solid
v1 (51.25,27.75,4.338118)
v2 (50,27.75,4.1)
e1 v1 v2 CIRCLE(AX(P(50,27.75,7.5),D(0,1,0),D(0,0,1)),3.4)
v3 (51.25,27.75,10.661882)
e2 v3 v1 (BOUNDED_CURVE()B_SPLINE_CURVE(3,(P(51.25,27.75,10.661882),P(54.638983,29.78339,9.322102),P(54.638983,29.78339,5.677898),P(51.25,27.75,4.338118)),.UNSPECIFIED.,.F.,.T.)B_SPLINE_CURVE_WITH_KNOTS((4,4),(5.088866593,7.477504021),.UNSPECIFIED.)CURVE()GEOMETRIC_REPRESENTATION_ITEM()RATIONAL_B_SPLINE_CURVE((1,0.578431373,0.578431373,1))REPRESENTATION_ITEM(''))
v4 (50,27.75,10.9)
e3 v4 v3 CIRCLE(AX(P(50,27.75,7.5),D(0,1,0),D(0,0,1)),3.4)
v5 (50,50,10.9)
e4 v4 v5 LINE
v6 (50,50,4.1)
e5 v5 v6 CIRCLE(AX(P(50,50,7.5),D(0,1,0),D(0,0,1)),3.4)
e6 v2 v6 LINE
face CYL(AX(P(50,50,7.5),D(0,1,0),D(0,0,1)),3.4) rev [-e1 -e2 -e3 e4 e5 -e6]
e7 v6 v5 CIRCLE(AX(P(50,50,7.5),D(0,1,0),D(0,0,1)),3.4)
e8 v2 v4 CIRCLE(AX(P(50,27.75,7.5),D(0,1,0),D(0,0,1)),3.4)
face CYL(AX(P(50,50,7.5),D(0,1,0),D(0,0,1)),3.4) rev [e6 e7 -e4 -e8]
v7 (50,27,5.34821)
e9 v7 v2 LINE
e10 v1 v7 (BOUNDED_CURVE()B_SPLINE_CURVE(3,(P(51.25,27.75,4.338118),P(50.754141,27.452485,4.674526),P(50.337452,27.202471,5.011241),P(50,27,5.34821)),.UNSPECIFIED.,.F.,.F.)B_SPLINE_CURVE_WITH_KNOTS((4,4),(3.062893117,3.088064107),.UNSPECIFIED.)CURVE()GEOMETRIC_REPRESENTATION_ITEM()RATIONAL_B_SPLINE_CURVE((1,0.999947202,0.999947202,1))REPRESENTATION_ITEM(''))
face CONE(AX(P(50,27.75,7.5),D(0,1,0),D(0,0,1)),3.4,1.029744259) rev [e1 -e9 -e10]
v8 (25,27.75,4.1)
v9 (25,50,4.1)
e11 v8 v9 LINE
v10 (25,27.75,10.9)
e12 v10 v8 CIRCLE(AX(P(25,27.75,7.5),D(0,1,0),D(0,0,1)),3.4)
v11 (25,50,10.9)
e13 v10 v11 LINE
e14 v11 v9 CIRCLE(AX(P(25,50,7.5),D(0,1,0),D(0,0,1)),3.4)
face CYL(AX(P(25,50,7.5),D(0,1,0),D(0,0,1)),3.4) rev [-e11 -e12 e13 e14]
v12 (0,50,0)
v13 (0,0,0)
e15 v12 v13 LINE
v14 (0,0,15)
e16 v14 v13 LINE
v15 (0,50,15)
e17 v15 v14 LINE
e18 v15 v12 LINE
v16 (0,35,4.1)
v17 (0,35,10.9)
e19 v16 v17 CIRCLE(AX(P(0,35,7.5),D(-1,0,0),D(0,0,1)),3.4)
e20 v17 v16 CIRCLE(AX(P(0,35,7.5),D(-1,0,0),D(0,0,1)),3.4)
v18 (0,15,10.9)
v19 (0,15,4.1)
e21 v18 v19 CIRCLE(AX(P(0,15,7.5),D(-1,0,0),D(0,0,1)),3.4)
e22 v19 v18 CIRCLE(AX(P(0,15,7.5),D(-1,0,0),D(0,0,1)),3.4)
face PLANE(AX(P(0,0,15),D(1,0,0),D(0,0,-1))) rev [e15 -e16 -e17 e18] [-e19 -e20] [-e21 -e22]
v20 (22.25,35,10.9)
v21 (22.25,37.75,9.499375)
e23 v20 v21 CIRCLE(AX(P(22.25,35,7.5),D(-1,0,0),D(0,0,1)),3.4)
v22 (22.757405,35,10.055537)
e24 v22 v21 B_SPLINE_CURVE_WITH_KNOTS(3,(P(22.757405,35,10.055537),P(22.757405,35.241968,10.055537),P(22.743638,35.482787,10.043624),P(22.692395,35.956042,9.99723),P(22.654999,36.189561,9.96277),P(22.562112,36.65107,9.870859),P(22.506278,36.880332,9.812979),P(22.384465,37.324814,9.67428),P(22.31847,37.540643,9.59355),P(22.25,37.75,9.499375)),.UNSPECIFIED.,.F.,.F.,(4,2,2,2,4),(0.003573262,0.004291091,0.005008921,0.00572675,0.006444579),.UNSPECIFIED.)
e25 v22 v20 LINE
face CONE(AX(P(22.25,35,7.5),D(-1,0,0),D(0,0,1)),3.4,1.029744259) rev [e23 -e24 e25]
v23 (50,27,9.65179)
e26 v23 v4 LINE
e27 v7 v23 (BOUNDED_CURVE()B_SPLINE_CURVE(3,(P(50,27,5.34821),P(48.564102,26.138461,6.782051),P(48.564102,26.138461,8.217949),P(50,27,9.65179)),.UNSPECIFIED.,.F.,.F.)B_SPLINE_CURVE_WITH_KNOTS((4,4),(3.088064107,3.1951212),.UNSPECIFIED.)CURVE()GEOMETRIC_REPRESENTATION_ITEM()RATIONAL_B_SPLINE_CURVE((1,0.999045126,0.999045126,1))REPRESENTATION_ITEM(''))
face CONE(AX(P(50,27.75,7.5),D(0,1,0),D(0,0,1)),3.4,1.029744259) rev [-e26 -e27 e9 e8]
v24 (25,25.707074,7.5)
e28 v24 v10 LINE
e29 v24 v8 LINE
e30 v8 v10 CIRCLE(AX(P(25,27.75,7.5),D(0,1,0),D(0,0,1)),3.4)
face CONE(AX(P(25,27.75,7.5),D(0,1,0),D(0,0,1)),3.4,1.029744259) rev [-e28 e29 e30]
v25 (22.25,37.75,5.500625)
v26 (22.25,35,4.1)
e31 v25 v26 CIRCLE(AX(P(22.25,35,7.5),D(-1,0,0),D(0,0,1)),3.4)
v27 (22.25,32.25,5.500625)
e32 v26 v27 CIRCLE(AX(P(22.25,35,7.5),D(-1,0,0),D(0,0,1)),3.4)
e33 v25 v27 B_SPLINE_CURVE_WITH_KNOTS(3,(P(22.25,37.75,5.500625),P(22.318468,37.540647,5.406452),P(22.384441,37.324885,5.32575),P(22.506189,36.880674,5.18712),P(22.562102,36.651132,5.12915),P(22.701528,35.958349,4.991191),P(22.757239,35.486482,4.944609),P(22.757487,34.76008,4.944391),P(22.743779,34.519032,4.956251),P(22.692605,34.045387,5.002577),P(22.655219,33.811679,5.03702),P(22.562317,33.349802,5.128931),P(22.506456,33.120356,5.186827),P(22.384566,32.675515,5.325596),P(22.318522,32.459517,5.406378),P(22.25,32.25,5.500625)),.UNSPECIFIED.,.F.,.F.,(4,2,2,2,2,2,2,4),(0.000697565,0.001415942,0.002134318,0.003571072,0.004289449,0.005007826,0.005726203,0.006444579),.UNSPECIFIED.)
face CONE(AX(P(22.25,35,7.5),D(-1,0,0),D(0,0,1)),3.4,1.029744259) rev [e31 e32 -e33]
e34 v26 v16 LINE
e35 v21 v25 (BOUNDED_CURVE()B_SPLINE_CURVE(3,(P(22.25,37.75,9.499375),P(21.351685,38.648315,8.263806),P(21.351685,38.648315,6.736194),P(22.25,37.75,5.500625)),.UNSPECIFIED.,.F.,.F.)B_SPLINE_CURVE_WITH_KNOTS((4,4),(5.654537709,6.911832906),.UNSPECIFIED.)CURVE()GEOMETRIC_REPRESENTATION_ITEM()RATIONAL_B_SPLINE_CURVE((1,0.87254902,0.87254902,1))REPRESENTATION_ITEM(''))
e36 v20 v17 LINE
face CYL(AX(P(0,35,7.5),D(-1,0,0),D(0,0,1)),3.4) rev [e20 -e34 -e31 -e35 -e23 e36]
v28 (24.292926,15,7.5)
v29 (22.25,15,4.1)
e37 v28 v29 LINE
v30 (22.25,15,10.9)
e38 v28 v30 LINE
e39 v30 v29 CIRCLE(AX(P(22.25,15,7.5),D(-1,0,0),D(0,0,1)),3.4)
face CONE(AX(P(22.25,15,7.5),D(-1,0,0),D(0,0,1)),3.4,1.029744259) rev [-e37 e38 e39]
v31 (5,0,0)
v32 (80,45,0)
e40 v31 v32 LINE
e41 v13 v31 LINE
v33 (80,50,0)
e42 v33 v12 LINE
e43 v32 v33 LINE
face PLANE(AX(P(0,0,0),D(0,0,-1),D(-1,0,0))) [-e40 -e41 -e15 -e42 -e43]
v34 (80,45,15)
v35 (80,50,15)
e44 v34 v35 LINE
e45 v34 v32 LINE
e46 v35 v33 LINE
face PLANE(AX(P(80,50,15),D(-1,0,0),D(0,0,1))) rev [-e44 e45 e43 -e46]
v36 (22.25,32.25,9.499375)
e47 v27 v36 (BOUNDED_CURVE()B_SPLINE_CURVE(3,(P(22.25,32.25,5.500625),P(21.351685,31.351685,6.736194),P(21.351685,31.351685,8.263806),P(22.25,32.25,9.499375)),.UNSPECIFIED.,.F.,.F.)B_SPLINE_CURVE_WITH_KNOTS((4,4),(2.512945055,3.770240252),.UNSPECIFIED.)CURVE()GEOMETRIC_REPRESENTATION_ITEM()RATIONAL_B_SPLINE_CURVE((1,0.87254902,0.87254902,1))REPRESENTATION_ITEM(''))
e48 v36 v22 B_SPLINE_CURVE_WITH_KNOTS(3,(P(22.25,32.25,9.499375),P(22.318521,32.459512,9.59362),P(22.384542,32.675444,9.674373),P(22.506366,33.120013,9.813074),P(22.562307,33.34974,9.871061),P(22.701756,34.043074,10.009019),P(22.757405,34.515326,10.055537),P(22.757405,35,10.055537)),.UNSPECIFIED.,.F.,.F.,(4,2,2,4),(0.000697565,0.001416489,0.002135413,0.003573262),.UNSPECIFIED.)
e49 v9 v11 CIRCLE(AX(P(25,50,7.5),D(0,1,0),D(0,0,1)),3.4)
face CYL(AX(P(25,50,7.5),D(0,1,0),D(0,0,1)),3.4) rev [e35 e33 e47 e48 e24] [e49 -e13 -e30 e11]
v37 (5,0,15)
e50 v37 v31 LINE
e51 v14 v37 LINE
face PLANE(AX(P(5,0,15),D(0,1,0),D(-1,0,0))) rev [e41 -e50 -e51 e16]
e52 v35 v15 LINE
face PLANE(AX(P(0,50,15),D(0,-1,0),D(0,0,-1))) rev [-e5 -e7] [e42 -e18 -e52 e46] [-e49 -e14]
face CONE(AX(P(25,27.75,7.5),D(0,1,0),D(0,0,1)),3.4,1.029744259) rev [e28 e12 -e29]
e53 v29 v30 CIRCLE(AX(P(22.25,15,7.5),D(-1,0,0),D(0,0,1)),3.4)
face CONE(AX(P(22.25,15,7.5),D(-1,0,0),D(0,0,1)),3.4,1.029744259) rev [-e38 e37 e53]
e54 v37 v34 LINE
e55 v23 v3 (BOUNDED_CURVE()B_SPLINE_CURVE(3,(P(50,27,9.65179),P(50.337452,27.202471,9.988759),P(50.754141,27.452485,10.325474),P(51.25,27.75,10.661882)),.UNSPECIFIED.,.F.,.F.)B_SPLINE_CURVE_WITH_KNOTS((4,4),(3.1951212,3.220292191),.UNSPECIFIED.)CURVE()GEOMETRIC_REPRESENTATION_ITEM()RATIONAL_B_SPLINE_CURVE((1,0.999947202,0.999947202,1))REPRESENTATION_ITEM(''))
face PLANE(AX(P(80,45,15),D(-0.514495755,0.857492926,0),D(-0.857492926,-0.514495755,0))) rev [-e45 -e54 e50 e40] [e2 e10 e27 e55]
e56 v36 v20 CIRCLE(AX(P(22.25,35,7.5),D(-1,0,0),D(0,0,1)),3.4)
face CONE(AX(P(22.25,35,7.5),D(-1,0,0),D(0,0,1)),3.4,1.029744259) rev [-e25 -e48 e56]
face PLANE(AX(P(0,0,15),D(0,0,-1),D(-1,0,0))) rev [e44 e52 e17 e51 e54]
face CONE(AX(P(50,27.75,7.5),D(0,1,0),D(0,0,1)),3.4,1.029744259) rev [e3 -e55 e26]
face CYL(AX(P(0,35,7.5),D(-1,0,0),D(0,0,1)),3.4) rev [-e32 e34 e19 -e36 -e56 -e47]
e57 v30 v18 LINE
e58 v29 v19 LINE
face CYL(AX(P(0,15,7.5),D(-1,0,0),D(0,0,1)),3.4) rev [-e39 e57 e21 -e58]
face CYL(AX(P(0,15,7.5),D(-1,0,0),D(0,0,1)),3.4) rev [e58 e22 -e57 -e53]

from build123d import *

# Parameters (mm, degrees)
BOSS_EXTRUDE1_DEPTH   = 15
M8_TAPPED_HOLE1_D     = 6.8
M8_TAPPED_HOLE1_DEPTH = 22.25
M8_TAPPED_HOLE1_TIP   = 2.042926105
M8_TAPPED_HOLE2_D     = 6.8
M8_TAPPED_HOLE2_DEPTH = 22.25
M8_TAPPED_HOLE2_TIP   = 2.042926105


with BuildPart() as part:
    # Sketch1 → Boss-Extrude1 (new body)
    with BuildSketch(Plane.XY):
        Polygon((0, 0), (0, 50), (80, 50), (80, 45), (5, 0), align=None)
    extrude(amount=BOSS_EXTRUDE1_DEPTH)

    # M8 Tapped Hole1
    with Locations(Plane(origin=(0, 50, 0), x_dir=(1, 0, 0), z_dir=(0, 1, 0))):
        with Locations((25, -7.5), (50, -7.5)):
            Hole(M8_TAPPED_HOLE1_D / 2, depth=M8_TAPPED_HOLE1_DEPTH)
            with Locations((0, 0, -(M8_TAPPED_HOLE1_DEPTH + M8_TAPPED_HOLE1_TIP / 2))):  # 118° drill point
                Cone(0, M8_TAPPED_HOLE1_D / 2, M8_TAPPED_HOLE1_TIP, mode=Mode.SUBTRACT)

    # M8 Tapped Hole2
    with Locations(Plane.ZY):
        with Locations((7.5, 35), (7.5, 15)):
            Hole(M8_TAPPED_HOLE2_D / 2, depth=M8_TAPPED_HOLE2_DEPTH)
            with Locations((0, 0, -(M8_TAPPED_HOLE2_DEPTH + M8_TAPPED_HOLE2_TIP / 2))):  # 118° drill point
                Cone(0, M8_TAPPED_HOLE2_D / 2, M8_TAPPED_HOLE2_TIP, mode=Mode.SUBTRACT)


solid = part.part
